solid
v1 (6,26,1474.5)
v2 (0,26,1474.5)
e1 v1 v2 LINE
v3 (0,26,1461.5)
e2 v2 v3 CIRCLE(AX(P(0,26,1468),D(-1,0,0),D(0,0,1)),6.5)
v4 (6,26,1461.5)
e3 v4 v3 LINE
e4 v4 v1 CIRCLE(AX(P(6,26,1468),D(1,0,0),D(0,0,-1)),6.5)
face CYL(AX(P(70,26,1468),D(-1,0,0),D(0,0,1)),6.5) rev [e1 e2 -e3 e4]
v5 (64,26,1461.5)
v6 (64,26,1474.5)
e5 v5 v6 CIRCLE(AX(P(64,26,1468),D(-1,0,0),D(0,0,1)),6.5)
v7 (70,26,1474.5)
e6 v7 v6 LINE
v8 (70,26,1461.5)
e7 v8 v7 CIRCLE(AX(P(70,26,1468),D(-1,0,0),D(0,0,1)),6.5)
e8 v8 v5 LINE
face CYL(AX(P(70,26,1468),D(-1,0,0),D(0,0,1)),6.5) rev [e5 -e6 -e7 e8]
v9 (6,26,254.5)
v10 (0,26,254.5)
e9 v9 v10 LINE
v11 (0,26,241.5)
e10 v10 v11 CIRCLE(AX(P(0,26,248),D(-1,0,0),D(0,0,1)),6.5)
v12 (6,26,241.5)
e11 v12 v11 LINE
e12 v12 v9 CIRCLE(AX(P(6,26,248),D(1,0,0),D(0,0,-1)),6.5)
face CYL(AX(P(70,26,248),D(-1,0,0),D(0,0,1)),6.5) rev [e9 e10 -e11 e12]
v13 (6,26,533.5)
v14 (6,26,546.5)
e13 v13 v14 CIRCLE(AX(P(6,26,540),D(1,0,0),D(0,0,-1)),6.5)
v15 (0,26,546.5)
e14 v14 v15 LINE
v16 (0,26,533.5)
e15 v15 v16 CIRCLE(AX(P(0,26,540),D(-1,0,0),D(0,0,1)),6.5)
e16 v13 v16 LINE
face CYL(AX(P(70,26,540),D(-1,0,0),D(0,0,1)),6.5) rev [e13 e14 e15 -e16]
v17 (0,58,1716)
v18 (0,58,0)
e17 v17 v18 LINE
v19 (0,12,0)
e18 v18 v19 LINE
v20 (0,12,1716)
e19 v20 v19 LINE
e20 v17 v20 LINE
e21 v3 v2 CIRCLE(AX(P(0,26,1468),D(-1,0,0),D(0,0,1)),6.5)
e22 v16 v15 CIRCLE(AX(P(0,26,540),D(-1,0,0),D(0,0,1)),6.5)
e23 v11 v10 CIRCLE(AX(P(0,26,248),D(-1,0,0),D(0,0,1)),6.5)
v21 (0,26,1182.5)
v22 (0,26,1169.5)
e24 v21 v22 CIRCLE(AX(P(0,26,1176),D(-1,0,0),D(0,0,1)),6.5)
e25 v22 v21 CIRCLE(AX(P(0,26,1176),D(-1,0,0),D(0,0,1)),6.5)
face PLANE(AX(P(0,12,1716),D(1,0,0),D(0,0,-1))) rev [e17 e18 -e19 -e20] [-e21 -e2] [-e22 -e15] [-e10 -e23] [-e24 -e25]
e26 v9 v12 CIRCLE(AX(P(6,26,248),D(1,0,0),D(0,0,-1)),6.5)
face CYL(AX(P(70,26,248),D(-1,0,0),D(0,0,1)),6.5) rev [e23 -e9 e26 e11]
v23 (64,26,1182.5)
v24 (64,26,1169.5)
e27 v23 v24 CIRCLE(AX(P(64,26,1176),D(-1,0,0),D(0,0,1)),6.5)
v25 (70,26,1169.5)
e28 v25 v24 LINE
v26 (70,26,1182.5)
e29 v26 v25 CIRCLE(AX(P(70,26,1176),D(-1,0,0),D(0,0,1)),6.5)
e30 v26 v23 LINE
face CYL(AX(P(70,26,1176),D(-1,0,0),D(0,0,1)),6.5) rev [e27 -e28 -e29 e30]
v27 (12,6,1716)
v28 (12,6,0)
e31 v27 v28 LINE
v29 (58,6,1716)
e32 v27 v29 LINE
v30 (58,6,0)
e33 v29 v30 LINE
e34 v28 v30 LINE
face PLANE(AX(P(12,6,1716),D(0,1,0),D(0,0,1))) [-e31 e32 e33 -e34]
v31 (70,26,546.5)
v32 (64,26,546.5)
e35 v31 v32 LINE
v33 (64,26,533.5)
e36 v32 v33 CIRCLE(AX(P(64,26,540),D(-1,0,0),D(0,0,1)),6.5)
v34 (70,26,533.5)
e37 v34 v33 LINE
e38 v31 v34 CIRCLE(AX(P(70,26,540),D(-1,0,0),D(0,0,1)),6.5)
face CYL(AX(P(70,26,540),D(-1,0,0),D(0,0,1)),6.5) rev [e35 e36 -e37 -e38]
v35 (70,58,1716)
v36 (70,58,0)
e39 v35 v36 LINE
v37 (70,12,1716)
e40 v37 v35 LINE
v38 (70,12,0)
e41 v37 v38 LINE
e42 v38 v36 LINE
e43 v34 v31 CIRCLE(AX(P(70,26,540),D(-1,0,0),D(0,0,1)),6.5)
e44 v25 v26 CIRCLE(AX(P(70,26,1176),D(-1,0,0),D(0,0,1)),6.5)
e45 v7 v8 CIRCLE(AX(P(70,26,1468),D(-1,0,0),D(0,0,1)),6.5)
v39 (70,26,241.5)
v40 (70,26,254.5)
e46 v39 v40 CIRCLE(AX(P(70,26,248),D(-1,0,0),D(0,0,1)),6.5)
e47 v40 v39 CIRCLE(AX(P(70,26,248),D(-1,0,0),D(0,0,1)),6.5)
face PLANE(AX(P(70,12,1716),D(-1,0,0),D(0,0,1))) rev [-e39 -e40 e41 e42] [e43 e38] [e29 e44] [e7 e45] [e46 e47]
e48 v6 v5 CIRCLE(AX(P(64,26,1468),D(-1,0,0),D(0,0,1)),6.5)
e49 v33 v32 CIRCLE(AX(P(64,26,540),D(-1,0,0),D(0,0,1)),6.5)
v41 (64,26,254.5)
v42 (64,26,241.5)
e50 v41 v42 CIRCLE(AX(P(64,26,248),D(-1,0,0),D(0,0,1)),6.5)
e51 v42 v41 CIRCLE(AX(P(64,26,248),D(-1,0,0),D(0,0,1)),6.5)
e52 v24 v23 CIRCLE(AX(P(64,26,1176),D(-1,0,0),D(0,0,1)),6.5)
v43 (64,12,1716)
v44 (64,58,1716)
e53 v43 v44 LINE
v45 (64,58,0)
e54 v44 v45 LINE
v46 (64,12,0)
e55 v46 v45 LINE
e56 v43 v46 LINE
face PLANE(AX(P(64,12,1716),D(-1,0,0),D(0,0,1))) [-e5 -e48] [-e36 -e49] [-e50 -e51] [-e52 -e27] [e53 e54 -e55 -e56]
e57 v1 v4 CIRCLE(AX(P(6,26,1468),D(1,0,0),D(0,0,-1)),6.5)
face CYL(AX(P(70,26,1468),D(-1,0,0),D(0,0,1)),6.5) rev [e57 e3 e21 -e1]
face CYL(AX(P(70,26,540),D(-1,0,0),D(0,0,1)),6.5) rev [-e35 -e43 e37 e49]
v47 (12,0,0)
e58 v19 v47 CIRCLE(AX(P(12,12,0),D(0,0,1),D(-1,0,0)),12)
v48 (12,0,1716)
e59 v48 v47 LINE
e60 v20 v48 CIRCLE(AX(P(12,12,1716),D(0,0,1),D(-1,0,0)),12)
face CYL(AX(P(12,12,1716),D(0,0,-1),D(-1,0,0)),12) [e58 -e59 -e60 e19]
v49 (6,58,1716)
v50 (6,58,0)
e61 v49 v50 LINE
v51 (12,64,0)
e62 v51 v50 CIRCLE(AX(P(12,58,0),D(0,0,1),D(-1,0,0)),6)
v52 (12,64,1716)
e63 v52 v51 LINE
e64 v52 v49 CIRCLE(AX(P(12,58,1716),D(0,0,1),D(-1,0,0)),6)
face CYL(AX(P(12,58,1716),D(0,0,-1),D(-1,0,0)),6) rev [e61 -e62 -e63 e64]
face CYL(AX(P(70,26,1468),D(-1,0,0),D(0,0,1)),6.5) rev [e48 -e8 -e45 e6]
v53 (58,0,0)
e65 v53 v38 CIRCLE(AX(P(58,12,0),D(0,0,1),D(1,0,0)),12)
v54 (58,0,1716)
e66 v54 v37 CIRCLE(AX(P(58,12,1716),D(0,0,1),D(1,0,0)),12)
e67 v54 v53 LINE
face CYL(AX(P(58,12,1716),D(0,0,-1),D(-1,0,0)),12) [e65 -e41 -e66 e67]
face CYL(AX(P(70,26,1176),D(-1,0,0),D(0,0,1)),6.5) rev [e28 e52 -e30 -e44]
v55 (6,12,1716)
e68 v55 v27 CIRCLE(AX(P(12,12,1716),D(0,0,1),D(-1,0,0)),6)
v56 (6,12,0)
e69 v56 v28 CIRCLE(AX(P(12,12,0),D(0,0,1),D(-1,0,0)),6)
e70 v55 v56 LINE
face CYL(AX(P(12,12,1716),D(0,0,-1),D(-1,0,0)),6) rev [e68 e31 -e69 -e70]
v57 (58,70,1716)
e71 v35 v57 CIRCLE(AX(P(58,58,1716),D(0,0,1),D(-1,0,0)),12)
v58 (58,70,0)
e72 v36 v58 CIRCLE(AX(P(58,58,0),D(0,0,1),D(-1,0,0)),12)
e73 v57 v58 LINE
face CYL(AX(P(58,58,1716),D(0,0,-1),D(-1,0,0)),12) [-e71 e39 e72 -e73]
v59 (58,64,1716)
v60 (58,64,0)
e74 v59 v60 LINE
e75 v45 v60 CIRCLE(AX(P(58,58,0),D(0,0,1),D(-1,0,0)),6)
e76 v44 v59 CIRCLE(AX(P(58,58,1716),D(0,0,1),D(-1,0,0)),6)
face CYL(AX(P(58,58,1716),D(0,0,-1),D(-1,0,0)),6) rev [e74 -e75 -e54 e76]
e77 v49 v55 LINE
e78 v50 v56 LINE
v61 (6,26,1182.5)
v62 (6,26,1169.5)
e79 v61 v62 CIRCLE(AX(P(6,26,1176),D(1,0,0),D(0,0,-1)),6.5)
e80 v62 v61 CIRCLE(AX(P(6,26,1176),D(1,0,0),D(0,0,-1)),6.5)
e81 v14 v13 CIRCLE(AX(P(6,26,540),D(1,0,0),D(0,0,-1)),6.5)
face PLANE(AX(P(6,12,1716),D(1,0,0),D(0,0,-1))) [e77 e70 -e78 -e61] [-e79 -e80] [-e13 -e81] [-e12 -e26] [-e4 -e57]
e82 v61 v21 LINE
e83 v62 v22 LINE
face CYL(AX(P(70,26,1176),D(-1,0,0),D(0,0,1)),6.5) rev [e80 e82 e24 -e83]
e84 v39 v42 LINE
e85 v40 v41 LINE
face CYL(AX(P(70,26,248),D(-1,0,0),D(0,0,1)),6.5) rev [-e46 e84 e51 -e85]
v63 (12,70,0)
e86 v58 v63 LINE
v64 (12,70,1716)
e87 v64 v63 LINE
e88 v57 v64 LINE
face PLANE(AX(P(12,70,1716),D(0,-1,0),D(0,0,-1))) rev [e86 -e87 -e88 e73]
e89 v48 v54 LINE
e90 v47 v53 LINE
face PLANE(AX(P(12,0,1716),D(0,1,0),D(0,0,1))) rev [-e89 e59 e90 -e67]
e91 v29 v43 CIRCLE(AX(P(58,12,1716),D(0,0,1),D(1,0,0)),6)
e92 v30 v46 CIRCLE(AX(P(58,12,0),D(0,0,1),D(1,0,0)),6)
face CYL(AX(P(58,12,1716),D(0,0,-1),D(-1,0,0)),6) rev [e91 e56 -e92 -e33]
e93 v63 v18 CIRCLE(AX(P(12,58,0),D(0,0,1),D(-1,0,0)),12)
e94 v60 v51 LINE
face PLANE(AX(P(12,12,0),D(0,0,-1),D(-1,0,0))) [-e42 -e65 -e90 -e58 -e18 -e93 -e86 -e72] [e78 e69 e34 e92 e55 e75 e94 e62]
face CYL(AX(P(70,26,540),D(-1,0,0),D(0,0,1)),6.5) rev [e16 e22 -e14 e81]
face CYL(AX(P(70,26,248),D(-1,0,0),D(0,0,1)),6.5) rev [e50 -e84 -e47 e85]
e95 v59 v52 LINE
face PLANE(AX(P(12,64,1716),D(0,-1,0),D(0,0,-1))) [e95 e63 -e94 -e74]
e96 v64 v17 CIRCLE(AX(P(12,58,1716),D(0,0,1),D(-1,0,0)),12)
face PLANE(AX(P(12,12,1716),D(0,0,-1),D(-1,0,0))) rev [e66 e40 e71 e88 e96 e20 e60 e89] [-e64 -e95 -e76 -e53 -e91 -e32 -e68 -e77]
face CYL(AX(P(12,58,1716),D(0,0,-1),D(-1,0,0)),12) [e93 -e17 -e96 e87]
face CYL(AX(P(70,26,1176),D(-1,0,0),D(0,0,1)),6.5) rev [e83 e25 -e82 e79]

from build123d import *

# Parameters (mm, degrees)
BOSS_EXTRUDE1_DEPTH = 1716
SKETCH2_R           = 6.5
CUT_EXTRUDE1_DEPTH  = 1719.853105998
LPATTERN1_COUNT     = 2
LPATTERN1_PITCH     = 928


with BuildPart() as part:
    # Sketch1 → Boss-Extrude1 (new body)
    with BuildSketch(Plane.XY):
        with BuildLine():
            Line((12, 0), (58, 0))
            ThreePointArc((58, 0), (66.485281374, 3.514718626), (70, 12))
            Line((70, 12), (70, 58))
            ThreePointArc((70, 58), (66.485281374, 66.485281374), (58, 70))
            Line((58, 70), (12, 70))
            ThreePointArc((12, 70), (3.514718626, 66.485281374), (0, 58))
            Line((0, 58), (0, 12))
            ThreePointArc((0, 12), (3.514718626, 3.514718626), (12, 0))
        make_face()
        with BuildLine():
            Line((12, 6), (58, 6))
            ThreePointArc((58, 6), (62.242640687, 7.757359313), (64, 12))
            Line((64, 12), (64, 58))
            ThreePointArc((64, 58), (62.242640687, 62.242640687), (58, 64))
            Line((58, 64), (12, 64))
            ThreePointArc((12, 64), (7.757359313, 62.242640687), (6, 58))
            Line((6, 58), (6, 12))
            ThreePointArc((6, 12), (7.757359313, 7.757359313), (12, 6))
        make_face(mode=Mode.SUBTRACT)
    extrude(amount=BOSS_EXTRUDE1_DEPTH)

    # Sketch2 → Cut-Extrude1 (cut, through all)
    with BuildSketch(Plane.ZY):
        with Locations((248, 26)):
            Circle(SKETCH2_R)
        with Locations((540, 26)):
            Circle(SKETCH2_R)
    cut_extrude1 = extrude(amount=-CUT_EXTRUDE1_DEPTH, mode=Mode.SUBTRACT)

    # LPattern1: Cut-Extrude1 ×2
    with Locations(*[(0, 0, i * LPATTERN1_PITCH) for i in range(1, LPATTERN1_COUNT)]):
        add(cut_extrude1, mode=Mode.SUBTRACT)


solid = part.part
